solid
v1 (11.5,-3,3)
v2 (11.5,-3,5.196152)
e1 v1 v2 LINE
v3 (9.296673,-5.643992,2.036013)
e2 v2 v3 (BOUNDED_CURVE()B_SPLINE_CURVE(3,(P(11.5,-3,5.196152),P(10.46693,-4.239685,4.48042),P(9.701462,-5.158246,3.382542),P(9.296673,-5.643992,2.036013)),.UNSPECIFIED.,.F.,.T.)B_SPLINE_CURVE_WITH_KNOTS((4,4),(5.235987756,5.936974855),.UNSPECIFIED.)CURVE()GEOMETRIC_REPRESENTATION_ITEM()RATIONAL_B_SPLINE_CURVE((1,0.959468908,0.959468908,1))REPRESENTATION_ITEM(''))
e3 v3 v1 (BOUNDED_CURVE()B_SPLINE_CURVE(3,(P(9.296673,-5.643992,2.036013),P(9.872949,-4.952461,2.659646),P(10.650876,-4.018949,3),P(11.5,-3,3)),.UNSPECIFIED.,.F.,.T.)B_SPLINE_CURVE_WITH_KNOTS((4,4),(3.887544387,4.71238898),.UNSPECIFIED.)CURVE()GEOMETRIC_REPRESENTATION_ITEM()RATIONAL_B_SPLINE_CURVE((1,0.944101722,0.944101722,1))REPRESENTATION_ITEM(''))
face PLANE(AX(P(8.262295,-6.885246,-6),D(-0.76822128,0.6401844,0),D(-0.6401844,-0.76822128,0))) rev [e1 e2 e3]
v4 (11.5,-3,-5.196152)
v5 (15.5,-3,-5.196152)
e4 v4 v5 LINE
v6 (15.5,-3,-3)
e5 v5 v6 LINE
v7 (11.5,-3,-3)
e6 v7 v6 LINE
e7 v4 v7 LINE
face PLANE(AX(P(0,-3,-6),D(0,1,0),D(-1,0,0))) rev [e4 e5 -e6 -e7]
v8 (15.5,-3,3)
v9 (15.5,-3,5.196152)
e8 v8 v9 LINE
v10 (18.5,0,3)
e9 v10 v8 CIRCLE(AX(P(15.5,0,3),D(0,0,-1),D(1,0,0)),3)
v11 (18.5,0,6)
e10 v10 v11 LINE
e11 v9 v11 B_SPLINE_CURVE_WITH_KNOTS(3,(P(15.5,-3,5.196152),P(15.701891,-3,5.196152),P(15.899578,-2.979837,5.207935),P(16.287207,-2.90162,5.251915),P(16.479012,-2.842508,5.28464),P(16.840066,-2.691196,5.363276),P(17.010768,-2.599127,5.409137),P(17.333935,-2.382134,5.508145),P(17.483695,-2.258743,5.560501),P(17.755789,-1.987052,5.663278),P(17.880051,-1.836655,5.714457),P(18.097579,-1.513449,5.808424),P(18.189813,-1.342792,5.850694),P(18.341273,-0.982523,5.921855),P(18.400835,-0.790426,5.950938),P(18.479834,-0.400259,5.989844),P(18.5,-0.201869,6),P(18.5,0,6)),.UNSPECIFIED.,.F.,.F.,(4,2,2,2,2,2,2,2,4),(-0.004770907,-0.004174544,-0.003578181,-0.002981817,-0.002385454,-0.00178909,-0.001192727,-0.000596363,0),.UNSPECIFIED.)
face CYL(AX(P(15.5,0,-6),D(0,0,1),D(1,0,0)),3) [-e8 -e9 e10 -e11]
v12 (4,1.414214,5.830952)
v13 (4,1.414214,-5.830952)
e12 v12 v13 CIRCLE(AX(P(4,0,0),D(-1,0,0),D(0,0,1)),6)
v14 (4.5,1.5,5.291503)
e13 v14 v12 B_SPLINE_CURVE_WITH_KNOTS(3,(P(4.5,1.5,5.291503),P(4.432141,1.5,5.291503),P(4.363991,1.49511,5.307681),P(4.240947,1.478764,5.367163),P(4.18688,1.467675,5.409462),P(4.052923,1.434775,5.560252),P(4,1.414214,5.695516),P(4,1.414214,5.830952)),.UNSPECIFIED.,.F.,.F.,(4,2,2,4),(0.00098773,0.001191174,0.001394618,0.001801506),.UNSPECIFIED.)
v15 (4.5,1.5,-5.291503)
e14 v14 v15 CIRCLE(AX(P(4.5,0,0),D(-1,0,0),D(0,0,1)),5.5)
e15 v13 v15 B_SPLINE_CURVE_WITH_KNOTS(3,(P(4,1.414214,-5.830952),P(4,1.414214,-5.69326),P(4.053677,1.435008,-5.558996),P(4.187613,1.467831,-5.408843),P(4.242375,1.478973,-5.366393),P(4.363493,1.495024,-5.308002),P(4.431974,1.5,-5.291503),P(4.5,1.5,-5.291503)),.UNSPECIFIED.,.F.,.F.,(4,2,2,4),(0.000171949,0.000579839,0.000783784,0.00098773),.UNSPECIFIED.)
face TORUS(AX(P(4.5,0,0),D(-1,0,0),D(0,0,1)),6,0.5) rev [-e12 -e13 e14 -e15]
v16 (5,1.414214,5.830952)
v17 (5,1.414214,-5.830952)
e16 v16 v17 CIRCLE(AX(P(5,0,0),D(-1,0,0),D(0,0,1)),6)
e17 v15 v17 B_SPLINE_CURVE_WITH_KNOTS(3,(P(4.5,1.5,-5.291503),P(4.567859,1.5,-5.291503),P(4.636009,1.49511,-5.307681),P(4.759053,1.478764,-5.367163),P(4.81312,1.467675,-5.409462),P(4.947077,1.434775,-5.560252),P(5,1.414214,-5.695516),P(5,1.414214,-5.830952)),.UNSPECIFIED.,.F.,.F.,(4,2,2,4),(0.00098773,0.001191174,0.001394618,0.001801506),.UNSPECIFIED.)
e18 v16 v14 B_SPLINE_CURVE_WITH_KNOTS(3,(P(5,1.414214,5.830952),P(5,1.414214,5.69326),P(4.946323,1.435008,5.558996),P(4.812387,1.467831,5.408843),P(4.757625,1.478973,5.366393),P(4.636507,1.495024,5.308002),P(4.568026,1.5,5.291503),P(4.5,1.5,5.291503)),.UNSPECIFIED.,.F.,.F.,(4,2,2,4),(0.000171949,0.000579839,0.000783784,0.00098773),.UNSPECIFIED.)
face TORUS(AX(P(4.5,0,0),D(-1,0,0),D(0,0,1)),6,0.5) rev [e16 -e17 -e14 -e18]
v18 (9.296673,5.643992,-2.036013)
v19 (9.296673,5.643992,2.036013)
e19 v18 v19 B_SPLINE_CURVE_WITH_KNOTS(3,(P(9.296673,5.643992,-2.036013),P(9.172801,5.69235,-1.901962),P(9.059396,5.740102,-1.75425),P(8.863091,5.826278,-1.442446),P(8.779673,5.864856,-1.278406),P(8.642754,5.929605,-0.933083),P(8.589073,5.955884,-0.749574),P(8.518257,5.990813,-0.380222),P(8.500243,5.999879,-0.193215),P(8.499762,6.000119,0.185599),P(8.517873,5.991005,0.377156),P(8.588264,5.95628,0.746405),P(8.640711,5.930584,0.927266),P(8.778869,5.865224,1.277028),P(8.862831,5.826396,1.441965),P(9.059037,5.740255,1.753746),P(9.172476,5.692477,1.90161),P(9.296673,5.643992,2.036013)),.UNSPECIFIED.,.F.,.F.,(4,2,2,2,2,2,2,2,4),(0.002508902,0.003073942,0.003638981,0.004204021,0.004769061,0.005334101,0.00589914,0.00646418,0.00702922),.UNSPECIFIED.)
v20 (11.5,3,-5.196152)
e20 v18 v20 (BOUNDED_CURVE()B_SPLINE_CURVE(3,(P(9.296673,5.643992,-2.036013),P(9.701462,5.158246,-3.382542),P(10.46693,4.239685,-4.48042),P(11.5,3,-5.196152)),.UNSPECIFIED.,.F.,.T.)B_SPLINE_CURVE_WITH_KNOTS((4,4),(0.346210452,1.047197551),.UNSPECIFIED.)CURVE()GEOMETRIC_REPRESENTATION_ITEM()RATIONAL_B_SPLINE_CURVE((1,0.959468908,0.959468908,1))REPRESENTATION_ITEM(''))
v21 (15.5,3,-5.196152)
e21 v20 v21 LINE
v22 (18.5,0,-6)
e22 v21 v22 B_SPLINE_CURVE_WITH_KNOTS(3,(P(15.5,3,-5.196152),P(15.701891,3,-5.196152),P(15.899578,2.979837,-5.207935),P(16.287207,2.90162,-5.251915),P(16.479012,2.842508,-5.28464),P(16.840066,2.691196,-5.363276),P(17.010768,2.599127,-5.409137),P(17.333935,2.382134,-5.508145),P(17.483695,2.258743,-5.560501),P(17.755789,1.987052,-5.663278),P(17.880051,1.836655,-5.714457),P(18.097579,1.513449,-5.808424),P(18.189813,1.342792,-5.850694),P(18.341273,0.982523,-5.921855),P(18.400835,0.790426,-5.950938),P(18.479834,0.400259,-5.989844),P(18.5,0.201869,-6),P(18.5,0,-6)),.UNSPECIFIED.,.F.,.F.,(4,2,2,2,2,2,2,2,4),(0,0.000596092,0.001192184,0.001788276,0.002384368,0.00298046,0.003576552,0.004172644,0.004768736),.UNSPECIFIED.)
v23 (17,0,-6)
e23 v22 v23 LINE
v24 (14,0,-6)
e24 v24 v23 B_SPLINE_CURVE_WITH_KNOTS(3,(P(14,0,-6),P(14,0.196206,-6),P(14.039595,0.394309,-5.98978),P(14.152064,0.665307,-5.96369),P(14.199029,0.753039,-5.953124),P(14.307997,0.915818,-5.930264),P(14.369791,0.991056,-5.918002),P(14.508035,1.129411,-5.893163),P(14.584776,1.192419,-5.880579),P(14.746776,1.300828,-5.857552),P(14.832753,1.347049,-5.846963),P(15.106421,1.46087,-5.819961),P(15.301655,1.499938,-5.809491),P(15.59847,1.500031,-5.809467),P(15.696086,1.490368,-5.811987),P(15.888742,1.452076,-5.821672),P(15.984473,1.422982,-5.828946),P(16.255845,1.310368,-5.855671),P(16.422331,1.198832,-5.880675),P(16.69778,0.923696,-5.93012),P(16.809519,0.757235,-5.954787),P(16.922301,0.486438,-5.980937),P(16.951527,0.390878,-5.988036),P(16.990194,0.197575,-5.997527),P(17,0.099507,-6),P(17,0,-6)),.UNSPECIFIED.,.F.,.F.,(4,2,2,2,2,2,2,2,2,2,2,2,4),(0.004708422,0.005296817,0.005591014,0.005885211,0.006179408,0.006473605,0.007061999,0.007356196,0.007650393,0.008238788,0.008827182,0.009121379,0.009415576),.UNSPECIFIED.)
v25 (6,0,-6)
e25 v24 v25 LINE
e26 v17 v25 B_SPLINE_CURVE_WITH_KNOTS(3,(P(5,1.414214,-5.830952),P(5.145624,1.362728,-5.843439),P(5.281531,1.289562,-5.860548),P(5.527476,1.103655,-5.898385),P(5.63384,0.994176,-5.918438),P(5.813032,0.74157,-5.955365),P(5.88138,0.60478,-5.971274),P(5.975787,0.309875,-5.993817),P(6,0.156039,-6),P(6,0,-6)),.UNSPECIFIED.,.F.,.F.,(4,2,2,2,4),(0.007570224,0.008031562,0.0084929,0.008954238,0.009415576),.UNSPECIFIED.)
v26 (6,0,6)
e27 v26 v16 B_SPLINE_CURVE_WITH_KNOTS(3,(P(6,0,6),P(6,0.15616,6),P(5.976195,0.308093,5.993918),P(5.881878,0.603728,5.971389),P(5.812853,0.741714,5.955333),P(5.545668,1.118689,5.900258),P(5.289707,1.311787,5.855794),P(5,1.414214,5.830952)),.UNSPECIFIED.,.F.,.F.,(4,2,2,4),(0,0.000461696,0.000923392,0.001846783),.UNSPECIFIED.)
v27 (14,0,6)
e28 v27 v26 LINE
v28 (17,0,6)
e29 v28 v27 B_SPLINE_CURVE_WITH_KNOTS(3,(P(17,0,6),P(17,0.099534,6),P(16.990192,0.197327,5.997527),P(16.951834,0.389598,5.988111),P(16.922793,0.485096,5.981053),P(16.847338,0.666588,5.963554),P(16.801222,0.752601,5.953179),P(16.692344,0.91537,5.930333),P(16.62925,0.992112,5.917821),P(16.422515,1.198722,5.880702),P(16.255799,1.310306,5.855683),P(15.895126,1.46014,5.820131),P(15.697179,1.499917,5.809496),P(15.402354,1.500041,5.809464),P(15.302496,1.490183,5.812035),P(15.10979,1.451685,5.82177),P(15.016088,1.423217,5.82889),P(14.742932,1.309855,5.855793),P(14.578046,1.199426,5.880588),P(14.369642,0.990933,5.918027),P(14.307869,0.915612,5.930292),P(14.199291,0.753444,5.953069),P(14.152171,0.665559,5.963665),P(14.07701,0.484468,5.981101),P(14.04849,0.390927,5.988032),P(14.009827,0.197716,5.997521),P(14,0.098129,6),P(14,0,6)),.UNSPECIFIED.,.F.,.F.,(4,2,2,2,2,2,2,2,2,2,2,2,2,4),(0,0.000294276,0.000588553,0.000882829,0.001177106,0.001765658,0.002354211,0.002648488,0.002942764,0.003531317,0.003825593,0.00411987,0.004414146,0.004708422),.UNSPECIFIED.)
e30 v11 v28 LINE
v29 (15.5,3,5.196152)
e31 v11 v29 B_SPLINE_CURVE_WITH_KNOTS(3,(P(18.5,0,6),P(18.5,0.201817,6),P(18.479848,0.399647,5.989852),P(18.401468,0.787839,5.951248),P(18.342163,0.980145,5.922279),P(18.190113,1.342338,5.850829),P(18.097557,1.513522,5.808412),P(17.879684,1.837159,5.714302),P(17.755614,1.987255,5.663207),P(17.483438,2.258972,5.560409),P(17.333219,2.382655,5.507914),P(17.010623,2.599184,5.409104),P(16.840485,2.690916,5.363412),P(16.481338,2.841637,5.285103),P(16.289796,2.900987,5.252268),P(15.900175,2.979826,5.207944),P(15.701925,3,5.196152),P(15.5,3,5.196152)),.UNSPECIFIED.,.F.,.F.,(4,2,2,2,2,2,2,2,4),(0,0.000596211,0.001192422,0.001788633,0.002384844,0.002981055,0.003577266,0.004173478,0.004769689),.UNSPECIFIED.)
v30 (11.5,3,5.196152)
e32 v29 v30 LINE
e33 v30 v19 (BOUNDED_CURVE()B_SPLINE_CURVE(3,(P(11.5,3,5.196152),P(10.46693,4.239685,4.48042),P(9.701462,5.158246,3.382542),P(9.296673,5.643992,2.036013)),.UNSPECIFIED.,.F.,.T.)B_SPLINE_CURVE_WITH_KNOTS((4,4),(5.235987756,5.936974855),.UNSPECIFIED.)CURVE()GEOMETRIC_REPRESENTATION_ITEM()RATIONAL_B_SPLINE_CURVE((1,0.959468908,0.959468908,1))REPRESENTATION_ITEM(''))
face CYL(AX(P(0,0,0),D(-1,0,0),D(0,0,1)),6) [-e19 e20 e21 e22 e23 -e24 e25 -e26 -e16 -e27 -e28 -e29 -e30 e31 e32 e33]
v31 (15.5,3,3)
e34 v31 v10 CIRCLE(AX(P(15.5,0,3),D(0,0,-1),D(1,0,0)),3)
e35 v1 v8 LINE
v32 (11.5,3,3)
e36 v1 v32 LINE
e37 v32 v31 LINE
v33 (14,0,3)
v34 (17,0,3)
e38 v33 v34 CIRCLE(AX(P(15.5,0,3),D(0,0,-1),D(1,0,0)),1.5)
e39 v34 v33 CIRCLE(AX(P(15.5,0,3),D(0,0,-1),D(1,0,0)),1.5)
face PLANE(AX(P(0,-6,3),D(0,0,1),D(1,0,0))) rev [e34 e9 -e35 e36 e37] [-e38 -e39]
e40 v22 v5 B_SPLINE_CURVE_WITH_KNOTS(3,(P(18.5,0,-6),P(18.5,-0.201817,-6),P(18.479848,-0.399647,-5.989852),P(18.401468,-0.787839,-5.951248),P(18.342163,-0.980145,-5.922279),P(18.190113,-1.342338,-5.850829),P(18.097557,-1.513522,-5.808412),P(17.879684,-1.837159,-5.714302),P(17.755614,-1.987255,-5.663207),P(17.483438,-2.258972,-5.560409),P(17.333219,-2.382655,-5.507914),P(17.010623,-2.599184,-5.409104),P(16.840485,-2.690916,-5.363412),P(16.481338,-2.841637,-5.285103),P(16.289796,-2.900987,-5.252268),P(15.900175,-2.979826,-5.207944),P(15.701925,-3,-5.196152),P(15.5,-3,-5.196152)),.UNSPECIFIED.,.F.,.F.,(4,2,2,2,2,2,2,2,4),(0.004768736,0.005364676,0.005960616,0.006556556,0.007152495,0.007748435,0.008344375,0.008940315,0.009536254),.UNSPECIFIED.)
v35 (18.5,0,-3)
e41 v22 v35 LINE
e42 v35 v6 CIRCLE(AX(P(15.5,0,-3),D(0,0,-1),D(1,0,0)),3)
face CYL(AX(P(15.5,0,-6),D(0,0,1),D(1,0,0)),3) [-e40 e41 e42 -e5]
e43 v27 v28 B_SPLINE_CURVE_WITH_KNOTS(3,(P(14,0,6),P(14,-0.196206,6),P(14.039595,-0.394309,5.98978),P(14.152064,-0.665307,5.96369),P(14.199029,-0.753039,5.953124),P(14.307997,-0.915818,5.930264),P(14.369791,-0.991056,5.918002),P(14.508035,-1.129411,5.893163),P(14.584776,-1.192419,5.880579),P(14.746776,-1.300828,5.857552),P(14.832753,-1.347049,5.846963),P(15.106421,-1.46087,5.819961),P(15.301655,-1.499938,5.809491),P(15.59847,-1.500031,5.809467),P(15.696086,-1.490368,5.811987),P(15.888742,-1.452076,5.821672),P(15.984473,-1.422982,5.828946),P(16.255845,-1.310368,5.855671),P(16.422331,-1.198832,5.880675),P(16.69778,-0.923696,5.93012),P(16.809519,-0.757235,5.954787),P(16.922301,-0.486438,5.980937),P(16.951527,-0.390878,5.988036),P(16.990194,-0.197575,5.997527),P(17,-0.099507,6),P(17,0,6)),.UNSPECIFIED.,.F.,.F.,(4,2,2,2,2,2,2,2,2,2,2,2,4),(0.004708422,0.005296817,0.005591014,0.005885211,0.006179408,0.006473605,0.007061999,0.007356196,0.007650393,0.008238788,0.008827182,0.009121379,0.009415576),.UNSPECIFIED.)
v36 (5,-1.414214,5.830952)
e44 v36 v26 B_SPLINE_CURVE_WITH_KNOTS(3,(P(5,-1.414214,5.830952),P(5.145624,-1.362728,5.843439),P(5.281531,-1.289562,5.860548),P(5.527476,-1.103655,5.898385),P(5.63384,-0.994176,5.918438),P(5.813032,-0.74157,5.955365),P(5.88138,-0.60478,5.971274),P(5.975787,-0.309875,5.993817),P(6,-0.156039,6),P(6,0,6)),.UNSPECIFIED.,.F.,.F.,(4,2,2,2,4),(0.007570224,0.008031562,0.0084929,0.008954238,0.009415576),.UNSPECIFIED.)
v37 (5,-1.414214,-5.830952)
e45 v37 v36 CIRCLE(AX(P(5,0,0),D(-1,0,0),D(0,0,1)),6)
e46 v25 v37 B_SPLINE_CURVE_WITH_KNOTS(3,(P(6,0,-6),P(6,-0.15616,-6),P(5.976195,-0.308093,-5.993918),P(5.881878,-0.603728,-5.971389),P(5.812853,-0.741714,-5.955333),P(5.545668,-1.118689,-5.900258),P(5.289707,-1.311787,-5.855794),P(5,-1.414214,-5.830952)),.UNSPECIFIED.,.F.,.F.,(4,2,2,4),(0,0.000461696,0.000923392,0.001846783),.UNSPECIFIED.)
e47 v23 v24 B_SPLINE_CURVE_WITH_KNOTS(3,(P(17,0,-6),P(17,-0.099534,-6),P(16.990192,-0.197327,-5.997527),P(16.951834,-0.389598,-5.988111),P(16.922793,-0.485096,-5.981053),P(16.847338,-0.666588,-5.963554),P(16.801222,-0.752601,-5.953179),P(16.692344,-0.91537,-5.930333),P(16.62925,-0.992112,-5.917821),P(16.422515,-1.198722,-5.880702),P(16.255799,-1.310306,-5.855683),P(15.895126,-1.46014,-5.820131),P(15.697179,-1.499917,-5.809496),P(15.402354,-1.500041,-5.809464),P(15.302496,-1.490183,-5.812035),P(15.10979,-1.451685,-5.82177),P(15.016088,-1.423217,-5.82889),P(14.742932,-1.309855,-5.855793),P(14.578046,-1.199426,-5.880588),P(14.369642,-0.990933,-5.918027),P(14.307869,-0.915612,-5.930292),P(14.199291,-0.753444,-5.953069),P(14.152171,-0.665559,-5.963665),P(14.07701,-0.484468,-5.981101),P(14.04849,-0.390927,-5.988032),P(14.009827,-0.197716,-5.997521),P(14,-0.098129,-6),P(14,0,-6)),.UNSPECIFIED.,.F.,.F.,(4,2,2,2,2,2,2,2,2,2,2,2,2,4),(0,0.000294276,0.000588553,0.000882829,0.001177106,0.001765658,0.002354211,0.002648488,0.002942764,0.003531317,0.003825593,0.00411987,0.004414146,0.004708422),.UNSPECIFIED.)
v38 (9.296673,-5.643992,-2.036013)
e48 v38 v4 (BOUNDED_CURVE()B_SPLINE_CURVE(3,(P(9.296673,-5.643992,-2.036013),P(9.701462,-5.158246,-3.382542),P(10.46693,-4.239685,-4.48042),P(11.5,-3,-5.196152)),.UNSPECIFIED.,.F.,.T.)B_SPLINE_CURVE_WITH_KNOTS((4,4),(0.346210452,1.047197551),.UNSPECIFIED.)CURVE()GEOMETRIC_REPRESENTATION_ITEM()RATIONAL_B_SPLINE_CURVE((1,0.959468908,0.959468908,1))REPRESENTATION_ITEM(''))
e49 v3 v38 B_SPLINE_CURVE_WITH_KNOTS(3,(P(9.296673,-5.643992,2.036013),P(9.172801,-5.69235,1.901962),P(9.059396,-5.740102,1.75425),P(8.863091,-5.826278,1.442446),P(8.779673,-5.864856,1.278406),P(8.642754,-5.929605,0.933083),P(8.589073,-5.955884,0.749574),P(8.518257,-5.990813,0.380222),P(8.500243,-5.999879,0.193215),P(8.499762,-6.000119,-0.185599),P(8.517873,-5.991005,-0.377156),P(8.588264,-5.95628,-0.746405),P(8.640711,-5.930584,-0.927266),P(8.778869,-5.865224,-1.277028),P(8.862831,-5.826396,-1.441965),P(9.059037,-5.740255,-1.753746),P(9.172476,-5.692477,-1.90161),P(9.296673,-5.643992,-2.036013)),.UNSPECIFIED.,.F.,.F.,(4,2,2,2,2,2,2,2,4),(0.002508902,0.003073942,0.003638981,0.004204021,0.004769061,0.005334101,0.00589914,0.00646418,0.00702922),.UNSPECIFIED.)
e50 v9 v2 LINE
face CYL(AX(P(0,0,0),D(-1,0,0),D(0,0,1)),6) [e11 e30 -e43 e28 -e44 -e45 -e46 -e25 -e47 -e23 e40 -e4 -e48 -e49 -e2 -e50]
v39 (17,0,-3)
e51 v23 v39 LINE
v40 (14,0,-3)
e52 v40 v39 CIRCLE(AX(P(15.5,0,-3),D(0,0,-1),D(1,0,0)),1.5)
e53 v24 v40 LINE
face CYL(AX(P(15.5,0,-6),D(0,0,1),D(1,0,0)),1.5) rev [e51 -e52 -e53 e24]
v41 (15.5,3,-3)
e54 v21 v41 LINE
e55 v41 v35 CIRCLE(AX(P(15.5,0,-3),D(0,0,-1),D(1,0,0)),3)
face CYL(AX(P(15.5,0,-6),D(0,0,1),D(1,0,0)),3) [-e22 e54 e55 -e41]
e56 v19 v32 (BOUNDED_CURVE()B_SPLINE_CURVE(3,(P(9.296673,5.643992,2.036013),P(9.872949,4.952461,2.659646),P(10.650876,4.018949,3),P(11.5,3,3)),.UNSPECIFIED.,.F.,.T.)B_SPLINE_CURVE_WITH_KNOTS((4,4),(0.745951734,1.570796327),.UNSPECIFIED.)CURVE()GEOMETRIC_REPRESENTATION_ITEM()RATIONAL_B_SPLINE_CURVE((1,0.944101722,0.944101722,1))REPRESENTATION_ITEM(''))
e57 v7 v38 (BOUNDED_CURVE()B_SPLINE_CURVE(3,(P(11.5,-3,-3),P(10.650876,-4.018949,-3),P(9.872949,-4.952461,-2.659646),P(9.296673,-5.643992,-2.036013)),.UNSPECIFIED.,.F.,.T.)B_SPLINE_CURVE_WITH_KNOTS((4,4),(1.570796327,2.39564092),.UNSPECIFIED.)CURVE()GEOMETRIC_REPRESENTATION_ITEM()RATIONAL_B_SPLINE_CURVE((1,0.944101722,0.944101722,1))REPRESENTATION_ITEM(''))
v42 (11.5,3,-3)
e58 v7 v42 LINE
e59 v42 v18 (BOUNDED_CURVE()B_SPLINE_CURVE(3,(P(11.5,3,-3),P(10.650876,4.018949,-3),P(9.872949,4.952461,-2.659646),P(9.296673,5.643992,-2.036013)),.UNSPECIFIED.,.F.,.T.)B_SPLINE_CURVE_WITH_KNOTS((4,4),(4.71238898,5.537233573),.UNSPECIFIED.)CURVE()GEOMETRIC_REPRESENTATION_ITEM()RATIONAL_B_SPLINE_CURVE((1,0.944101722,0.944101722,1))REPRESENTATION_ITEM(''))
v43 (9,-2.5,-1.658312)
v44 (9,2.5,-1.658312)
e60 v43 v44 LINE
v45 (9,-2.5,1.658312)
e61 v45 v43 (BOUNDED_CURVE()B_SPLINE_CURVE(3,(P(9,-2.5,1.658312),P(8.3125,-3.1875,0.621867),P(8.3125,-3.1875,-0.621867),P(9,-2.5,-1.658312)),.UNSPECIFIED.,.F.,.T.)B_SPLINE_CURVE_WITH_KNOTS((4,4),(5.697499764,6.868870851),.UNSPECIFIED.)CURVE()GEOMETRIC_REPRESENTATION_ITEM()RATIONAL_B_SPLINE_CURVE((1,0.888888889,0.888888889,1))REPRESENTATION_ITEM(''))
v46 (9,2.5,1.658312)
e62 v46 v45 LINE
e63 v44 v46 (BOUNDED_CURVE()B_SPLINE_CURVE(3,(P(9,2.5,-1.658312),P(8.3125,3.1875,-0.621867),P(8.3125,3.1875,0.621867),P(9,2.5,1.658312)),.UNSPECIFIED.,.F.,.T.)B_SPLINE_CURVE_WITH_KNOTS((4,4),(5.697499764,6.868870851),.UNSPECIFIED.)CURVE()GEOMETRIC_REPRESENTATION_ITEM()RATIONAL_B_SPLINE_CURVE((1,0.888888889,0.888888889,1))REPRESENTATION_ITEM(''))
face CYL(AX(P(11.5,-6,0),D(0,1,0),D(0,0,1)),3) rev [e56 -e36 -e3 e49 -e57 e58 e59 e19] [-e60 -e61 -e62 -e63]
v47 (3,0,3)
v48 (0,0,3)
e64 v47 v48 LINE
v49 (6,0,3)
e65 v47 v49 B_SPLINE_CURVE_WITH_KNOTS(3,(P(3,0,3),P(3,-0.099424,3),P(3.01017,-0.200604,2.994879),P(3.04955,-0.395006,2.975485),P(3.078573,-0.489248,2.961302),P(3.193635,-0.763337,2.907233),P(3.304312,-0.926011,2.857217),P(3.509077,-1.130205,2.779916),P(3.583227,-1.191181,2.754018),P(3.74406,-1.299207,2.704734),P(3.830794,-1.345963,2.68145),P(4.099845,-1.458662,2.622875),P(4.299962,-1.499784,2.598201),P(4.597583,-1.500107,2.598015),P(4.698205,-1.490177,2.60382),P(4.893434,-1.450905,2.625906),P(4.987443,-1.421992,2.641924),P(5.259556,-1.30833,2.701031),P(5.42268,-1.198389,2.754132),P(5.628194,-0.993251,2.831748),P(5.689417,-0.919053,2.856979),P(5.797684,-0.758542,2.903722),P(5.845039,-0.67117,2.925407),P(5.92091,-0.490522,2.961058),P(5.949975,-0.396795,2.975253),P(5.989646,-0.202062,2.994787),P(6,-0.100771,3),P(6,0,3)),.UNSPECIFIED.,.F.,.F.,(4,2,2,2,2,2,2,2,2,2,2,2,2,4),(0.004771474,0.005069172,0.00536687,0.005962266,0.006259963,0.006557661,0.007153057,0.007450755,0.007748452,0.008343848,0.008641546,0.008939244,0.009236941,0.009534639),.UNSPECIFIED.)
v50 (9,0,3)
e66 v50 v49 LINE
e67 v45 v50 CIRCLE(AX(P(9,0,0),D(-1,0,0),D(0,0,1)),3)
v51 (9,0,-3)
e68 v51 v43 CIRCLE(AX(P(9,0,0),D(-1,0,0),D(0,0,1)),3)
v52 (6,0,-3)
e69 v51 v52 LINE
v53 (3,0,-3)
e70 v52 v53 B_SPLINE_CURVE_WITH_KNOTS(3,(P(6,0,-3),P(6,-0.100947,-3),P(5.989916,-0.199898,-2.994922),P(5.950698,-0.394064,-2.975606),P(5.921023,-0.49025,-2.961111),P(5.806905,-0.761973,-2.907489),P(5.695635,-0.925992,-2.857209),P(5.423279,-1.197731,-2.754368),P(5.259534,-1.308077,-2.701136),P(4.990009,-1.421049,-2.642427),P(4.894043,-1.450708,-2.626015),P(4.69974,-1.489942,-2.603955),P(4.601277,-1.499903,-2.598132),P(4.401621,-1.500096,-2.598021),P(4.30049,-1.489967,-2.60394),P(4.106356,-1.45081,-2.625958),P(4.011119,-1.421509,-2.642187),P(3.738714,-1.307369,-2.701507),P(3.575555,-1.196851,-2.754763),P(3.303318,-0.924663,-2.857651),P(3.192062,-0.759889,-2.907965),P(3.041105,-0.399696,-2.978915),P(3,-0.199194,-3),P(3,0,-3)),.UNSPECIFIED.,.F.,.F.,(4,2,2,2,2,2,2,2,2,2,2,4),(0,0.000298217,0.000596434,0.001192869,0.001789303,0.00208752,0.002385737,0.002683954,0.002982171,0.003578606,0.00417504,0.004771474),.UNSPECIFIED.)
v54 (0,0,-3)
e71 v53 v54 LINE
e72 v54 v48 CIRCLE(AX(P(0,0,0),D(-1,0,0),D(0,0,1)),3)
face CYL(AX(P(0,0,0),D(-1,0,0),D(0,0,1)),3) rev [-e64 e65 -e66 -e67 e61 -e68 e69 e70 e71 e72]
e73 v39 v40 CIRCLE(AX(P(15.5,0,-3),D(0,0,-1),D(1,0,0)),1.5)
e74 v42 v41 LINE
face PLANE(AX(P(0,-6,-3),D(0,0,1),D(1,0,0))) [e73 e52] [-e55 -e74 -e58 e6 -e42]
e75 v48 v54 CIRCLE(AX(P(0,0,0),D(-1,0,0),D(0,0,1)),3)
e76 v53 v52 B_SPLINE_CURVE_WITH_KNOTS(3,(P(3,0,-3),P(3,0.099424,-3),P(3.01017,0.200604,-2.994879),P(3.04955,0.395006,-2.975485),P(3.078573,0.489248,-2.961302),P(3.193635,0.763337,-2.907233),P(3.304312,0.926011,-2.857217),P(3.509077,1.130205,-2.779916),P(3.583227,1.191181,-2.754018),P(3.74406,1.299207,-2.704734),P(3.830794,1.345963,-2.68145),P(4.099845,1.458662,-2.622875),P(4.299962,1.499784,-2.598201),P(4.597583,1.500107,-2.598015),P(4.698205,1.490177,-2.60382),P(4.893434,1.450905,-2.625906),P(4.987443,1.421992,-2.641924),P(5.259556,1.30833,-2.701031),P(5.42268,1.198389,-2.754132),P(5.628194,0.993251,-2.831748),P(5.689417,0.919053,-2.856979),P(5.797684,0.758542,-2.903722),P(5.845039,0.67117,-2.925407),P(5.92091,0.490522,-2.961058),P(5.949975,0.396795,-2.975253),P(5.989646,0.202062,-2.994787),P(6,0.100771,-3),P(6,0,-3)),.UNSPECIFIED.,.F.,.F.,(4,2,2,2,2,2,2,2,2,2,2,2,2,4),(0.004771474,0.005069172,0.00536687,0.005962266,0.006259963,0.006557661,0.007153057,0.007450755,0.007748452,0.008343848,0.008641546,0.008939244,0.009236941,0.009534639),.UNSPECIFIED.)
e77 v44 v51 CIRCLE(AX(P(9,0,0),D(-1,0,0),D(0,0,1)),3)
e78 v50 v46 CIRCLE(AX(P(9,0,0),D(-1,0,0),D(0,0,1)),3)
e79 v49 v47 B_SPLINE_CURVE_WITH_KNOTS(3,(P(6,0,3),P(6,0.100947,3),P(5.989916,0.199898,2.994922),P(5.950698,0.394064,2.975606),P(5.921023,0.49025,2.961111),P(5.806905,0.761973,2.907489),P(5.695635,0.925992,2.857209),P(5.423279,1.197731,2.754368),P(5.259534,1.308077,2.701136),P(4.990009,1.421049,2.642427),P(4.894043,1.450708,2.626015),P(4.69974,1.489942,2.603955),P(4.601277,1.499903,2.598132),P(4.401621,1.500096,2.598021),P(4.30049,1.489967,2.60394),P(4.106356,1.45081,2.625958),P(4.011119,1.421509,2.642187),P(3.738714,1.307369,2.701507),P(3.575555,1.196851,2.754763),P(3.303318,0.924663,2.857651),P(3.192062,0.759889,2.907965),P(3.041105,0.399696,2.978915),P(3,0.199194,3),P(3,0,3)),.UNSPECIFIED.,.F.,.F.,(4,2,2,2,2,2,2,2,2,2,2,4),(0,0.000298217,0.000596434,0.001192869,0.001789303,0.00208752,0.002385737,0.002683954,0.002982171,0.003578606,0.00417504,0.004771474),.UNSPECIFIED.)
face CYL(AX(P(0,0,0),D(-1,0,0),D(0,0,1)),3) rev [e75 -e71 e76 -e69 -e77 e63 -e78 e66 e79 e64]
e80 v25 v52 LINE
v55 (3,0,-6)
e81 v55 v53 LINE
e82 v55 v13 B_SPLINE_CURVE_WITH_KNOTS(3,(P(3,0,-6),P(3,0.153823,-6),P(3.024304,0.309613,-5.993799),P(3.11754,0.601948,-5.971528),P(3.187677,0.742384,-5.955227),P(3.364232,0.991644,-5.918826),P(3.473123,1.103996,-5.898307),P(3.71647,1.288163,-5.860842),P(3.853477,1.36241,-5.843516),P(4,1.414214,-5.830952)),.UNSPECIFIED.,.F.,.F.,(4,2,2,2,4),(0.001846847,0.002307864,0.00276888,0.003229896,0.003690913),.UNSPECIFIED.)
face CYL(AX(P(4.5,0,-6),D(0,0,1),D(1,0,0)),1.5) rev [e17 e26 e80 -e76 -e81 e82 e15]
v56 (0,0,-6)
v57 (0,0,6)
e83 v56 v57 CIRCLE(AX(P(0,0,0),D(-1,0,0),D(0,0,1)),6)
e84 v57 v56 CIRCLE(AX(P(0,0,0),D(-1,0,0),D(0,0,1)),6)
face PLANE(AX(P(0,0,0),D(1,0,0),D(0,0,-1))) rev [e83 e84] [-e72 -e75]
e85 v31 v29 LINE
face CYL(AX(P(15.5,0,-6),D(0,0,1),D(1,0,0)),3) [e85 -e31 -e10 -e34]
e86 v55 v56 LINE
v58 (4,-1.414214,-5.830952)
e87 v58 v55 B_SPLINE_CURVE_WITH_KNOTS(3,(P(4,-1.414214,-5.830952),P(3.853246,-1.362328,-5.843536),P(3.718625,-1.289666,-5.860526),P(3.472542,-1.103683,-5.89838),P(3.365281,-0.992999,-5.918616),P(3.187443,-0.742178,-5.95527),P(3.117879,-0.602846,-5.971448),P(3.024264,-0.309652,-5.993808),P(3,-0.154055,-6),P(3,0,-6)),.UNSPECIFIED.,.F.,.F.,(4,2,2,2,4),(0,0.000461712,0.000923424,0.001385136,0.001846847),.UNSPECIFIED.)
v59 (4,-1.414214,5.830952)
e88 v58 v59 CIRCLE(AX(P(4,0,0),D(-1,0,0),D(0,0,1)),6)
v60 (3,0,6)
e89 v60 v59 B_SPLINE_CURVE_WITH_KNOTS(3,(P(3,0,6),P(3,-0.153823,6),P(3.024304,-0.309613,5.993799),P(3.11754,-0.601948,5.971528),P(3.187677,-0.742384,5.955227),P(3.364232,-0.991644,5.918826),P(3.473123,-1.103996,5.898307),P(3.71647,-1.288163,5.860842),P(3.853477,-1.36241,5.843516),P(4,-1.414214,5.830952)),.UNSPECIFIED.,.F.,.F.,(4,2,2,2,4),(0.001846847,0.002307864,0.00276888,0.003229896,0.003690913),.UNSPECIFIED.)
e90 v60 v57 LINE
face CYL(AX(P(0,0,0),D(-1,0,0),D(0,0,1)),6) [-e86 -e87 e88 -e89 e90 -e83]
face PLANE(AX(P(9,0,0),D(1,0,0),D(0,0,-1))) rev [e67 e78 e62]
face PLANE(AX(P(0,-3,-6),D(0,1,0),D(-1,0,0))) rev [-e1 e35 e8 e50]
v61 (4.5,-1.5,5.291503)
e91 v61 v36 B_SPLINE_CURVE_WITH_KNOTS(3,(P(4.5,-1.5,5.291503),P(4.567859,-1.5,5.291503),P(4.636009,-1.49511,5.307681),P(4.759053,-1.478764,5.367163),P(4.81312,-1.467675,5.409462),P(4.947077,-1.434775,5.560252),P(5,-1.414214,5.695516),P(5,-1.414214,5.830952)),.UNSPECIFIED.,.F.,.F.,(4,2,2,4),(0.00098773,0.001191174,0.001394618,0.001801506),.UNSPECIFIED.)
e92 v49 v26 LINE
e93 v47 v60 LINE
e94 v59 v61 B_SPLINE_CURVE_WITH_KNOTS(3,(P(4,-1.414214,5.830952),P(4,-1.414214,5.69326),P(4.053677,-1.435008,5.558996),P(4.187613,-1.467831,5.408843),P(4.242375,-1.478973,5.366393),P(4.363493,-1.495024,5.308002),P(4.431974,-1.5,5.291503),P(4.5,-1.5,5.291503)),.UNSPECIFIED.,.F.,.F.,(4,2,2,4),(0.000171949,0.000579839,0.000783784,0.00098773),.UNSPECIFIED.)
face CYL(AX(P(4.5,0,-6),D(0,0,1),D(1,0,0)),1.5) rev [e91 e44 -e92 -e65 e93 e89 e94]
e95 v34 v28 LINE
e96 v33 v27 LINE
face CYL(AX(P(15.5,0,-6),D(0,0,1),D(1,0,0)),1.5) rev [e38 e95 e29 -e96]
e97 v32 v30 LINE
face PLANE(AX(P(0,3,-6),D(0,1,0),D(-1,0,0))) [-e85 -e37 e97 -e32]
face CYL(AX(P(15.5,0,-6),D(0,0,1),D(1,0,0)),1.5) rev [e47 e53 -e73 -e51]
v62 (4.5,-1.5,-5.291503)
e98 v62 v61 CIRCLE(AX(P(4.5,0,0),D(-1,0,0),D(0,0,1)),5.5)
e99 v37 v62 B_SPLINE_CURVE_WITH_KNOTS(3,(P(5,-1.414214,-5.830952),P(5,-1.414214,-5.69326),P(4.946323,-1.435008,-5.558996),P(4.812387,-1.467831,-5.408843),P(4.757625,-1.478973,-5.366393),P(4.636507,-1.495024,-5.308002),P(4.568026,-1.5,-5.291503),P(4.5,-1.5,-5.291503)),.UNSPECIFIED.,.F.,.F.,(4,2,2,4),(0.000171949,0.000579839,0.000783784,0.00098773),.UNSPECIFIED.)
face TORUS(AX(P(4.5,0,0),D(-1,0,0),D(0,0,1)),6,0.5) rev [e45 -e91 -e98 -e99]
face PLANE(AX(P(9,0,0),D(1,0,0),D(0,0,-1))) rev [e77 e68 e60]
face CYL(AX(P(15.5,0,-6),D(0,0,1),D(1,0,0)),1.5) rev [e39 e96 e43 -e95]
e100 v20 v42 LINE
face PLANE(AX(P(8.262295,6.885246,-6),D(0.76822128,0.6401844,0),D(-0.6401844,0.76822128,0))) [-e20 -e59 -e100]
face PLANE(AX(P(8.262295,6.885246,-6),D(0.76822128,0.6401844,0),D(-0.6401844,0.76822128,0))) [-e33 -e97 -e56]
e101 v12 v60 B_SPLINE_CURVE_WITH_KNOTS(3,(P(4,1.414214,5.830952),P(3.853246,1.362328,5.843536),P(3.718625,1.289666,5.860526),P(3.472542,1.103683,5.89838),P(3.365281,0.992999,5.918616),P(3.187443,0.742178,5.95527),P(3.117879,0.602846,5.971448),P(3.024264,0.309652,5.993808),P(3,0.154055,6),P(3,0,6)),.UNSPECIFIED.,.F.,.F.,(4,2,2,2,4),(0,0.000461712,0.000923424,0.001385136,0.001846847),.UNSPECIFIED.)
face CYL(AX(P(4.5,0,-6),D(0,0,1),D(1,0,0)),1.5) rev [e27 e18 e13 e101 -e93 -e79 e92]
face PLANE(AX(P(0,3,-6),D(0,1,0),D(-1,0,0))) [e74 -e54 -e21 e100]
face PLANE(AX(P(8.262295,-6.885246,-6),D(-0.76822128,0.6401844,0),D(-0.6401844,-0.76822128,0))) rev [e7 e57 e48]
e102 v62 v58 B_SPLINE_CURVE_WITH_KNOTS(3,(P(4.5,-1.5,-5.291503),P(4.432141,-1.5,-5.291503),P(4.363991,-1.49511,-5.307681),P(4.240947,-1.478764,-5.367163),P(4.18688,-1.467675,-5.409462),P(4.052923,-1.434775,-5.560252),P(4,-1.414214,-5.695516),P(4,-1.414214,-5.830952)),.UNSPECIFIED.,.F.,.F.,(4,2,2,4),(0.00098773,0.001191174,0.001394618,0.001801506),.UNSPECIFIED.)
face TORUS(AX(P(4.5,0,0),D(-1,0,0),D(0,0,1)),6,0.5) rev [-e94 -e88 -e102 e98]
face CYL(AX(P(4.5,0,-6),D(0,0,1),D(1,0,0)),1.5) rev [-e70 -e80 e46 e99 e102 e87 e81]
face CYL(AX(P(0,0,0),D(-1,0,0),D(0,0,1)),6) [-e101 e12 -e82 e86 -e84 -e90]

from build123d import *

# Parameters (mm, degrees)
CUT_EXTRUDE_1_DEPTH      = 21.353132437
CUT_EXTRUDE_1_DEPTH_BACK = 21.353132437
CUT_EXTRUDE_2_DEPTH      = 21.353132587
CUT_EXTRUDE_2_DEPTH_BACK = 21.353132587
SKETCH_2_R               = 3


with BuildPart() as part:
    # 草图1 one side → 旋转3 (revolve)
    with BuildSketch(Plane.XY, mode=Mode.PRIVATE) as revolve_3_sk:
        with BuildLine():
            Line((18.5, 0), (18.5, 6))
            Line((18.5, 6), (5, 6))
            ThreePointArc((5, 6), (4.5, 5.5), (4, 6))
            Line((4, 6), (0, 6))
            Line((0, 6), (0, 3))
            Line((0, 3), (9, 3))
            Line((9, 3), (9, 0))
            Line((9, 0), (14, 0))
            ThreePointArc((14, 0), (15.5, 1.5), (17, 0))
            Line((17, 0), (18.5, 0))
        make_face()
    revolve(revolve_3_sk.sketch.rotate(Axis((0, 0, 0), (1, 0, 0)), 90), axis=Axis((0, 0, 0), (1, 0, 0)))

    # 草图1<11> → 切除-拉伸1 (cut, two sides: drawn at the far end of the back side and taken through both)
    with BuildSketch(Plane.XY.offset(-CUT_EXTRUDE_1_DEPTH_BACK)):
        with BuildLine():
            Line((11.5, 3), (15.5, 3))
            ThreePointArc((15.5, 3), (17.621320344, 2.121320344), (18.5, 0))
            Line((18.5, 0), (18.5, 6))
            Line((18.5, 6), (9, 6))
            Line((9, 6), (11.5, 3))
        make_face()
        with BuildLine():
            Line((18.5, -6), (18.5, 0))
            ThreePointArc((18.5, 0), (17.621320344, -2.121320344), (15.5, -3))
            Line((15.5, -3), (11.5, -3))
            Line((11.5, -3), (9, -6))
            Line((9, -6), (18.5, -6))
        make_face()
        with BuildLine():
            ThreePointArc((14, 0), (15.5, -1.5), (17, 0))
            Line((17, 0), (14, 0))
        make_face()
        with BuildLine():
            Line((14, 0), (17, 0))
            ThreePointArc((17, 0), (15.5, 1.5), (14, 0))
        make_face()
        with BuildLine():
            ThreePointArc((3, 0), (4.5, -1.5), (6, 0))
            Line((6, 0), (3, 0))
        make_face()
        with BuildLine():
            Line((3, 0), (6, 0))
            ThreePointArc((6, 0), (4.5, 1.5), (3, 0))
        make_face()
        with BuildLine():
            ThreePointArc((3, 0), (4.5, -1.5), (6, 0))
            Line((6, 0), (3, 0))
        make_face()
        with BuildLine():
            Line((3, 0), (6, 0))
            ThreePointArc((6, 0), (4.5, 1.5), (3, 0))
        make_face()
        with BuildLine():
            ThreePointArc((14, 0), (15.5, -1.5), (17, 0))
            Line((17, 0), (14, 0))
        make_face()
        with BuildLine():
            Line((14, 0), (17, 0))
            ThreePointArc((17, 0), (15.5, 1.5), (14, 0))
        make_face()
    extrude(amount=CUT_EXTRUDE_1_DEPTH + CUT_EXTRUDE_1_DEPTH_BACK, mode=Mode.SUBTRACT)

    # 草图2 → 切除-拉伸2 (cut, two sides: drawn at the far end of the back side and taken through both)
    with BuildSketch(Plane(origin=(0, 0, 0), x_dir=(1, 0, 0), z_dir=(0, 1, 0)).offset(-CUT_EXTRUDE_2_DEPTH_BACK)):
        with Locations((11.5, 0)):
            Circle(SKETCH_2_R)
        with BuildLine():
            Line((18.5, 3), (11.5, 3))
            ThreePointArc((11.5, 3), (13.621320344, 2.121320344), (14.5, 0))
            ThreePointArc((14.5, 0), (13.621320344, -2.121320344), (11.5, -3))
            Line((11.5, -3), (18.5, -3))
            Line((18.5, -3), (18.5, 3))
        make_face()
    extrude(amount=CUT_EXTRUDE_2_DEPTH + CUT_EXTRUDE_2_DEPTH_BACK, mode=Mode.SUBTRACT)


solid = part.part
